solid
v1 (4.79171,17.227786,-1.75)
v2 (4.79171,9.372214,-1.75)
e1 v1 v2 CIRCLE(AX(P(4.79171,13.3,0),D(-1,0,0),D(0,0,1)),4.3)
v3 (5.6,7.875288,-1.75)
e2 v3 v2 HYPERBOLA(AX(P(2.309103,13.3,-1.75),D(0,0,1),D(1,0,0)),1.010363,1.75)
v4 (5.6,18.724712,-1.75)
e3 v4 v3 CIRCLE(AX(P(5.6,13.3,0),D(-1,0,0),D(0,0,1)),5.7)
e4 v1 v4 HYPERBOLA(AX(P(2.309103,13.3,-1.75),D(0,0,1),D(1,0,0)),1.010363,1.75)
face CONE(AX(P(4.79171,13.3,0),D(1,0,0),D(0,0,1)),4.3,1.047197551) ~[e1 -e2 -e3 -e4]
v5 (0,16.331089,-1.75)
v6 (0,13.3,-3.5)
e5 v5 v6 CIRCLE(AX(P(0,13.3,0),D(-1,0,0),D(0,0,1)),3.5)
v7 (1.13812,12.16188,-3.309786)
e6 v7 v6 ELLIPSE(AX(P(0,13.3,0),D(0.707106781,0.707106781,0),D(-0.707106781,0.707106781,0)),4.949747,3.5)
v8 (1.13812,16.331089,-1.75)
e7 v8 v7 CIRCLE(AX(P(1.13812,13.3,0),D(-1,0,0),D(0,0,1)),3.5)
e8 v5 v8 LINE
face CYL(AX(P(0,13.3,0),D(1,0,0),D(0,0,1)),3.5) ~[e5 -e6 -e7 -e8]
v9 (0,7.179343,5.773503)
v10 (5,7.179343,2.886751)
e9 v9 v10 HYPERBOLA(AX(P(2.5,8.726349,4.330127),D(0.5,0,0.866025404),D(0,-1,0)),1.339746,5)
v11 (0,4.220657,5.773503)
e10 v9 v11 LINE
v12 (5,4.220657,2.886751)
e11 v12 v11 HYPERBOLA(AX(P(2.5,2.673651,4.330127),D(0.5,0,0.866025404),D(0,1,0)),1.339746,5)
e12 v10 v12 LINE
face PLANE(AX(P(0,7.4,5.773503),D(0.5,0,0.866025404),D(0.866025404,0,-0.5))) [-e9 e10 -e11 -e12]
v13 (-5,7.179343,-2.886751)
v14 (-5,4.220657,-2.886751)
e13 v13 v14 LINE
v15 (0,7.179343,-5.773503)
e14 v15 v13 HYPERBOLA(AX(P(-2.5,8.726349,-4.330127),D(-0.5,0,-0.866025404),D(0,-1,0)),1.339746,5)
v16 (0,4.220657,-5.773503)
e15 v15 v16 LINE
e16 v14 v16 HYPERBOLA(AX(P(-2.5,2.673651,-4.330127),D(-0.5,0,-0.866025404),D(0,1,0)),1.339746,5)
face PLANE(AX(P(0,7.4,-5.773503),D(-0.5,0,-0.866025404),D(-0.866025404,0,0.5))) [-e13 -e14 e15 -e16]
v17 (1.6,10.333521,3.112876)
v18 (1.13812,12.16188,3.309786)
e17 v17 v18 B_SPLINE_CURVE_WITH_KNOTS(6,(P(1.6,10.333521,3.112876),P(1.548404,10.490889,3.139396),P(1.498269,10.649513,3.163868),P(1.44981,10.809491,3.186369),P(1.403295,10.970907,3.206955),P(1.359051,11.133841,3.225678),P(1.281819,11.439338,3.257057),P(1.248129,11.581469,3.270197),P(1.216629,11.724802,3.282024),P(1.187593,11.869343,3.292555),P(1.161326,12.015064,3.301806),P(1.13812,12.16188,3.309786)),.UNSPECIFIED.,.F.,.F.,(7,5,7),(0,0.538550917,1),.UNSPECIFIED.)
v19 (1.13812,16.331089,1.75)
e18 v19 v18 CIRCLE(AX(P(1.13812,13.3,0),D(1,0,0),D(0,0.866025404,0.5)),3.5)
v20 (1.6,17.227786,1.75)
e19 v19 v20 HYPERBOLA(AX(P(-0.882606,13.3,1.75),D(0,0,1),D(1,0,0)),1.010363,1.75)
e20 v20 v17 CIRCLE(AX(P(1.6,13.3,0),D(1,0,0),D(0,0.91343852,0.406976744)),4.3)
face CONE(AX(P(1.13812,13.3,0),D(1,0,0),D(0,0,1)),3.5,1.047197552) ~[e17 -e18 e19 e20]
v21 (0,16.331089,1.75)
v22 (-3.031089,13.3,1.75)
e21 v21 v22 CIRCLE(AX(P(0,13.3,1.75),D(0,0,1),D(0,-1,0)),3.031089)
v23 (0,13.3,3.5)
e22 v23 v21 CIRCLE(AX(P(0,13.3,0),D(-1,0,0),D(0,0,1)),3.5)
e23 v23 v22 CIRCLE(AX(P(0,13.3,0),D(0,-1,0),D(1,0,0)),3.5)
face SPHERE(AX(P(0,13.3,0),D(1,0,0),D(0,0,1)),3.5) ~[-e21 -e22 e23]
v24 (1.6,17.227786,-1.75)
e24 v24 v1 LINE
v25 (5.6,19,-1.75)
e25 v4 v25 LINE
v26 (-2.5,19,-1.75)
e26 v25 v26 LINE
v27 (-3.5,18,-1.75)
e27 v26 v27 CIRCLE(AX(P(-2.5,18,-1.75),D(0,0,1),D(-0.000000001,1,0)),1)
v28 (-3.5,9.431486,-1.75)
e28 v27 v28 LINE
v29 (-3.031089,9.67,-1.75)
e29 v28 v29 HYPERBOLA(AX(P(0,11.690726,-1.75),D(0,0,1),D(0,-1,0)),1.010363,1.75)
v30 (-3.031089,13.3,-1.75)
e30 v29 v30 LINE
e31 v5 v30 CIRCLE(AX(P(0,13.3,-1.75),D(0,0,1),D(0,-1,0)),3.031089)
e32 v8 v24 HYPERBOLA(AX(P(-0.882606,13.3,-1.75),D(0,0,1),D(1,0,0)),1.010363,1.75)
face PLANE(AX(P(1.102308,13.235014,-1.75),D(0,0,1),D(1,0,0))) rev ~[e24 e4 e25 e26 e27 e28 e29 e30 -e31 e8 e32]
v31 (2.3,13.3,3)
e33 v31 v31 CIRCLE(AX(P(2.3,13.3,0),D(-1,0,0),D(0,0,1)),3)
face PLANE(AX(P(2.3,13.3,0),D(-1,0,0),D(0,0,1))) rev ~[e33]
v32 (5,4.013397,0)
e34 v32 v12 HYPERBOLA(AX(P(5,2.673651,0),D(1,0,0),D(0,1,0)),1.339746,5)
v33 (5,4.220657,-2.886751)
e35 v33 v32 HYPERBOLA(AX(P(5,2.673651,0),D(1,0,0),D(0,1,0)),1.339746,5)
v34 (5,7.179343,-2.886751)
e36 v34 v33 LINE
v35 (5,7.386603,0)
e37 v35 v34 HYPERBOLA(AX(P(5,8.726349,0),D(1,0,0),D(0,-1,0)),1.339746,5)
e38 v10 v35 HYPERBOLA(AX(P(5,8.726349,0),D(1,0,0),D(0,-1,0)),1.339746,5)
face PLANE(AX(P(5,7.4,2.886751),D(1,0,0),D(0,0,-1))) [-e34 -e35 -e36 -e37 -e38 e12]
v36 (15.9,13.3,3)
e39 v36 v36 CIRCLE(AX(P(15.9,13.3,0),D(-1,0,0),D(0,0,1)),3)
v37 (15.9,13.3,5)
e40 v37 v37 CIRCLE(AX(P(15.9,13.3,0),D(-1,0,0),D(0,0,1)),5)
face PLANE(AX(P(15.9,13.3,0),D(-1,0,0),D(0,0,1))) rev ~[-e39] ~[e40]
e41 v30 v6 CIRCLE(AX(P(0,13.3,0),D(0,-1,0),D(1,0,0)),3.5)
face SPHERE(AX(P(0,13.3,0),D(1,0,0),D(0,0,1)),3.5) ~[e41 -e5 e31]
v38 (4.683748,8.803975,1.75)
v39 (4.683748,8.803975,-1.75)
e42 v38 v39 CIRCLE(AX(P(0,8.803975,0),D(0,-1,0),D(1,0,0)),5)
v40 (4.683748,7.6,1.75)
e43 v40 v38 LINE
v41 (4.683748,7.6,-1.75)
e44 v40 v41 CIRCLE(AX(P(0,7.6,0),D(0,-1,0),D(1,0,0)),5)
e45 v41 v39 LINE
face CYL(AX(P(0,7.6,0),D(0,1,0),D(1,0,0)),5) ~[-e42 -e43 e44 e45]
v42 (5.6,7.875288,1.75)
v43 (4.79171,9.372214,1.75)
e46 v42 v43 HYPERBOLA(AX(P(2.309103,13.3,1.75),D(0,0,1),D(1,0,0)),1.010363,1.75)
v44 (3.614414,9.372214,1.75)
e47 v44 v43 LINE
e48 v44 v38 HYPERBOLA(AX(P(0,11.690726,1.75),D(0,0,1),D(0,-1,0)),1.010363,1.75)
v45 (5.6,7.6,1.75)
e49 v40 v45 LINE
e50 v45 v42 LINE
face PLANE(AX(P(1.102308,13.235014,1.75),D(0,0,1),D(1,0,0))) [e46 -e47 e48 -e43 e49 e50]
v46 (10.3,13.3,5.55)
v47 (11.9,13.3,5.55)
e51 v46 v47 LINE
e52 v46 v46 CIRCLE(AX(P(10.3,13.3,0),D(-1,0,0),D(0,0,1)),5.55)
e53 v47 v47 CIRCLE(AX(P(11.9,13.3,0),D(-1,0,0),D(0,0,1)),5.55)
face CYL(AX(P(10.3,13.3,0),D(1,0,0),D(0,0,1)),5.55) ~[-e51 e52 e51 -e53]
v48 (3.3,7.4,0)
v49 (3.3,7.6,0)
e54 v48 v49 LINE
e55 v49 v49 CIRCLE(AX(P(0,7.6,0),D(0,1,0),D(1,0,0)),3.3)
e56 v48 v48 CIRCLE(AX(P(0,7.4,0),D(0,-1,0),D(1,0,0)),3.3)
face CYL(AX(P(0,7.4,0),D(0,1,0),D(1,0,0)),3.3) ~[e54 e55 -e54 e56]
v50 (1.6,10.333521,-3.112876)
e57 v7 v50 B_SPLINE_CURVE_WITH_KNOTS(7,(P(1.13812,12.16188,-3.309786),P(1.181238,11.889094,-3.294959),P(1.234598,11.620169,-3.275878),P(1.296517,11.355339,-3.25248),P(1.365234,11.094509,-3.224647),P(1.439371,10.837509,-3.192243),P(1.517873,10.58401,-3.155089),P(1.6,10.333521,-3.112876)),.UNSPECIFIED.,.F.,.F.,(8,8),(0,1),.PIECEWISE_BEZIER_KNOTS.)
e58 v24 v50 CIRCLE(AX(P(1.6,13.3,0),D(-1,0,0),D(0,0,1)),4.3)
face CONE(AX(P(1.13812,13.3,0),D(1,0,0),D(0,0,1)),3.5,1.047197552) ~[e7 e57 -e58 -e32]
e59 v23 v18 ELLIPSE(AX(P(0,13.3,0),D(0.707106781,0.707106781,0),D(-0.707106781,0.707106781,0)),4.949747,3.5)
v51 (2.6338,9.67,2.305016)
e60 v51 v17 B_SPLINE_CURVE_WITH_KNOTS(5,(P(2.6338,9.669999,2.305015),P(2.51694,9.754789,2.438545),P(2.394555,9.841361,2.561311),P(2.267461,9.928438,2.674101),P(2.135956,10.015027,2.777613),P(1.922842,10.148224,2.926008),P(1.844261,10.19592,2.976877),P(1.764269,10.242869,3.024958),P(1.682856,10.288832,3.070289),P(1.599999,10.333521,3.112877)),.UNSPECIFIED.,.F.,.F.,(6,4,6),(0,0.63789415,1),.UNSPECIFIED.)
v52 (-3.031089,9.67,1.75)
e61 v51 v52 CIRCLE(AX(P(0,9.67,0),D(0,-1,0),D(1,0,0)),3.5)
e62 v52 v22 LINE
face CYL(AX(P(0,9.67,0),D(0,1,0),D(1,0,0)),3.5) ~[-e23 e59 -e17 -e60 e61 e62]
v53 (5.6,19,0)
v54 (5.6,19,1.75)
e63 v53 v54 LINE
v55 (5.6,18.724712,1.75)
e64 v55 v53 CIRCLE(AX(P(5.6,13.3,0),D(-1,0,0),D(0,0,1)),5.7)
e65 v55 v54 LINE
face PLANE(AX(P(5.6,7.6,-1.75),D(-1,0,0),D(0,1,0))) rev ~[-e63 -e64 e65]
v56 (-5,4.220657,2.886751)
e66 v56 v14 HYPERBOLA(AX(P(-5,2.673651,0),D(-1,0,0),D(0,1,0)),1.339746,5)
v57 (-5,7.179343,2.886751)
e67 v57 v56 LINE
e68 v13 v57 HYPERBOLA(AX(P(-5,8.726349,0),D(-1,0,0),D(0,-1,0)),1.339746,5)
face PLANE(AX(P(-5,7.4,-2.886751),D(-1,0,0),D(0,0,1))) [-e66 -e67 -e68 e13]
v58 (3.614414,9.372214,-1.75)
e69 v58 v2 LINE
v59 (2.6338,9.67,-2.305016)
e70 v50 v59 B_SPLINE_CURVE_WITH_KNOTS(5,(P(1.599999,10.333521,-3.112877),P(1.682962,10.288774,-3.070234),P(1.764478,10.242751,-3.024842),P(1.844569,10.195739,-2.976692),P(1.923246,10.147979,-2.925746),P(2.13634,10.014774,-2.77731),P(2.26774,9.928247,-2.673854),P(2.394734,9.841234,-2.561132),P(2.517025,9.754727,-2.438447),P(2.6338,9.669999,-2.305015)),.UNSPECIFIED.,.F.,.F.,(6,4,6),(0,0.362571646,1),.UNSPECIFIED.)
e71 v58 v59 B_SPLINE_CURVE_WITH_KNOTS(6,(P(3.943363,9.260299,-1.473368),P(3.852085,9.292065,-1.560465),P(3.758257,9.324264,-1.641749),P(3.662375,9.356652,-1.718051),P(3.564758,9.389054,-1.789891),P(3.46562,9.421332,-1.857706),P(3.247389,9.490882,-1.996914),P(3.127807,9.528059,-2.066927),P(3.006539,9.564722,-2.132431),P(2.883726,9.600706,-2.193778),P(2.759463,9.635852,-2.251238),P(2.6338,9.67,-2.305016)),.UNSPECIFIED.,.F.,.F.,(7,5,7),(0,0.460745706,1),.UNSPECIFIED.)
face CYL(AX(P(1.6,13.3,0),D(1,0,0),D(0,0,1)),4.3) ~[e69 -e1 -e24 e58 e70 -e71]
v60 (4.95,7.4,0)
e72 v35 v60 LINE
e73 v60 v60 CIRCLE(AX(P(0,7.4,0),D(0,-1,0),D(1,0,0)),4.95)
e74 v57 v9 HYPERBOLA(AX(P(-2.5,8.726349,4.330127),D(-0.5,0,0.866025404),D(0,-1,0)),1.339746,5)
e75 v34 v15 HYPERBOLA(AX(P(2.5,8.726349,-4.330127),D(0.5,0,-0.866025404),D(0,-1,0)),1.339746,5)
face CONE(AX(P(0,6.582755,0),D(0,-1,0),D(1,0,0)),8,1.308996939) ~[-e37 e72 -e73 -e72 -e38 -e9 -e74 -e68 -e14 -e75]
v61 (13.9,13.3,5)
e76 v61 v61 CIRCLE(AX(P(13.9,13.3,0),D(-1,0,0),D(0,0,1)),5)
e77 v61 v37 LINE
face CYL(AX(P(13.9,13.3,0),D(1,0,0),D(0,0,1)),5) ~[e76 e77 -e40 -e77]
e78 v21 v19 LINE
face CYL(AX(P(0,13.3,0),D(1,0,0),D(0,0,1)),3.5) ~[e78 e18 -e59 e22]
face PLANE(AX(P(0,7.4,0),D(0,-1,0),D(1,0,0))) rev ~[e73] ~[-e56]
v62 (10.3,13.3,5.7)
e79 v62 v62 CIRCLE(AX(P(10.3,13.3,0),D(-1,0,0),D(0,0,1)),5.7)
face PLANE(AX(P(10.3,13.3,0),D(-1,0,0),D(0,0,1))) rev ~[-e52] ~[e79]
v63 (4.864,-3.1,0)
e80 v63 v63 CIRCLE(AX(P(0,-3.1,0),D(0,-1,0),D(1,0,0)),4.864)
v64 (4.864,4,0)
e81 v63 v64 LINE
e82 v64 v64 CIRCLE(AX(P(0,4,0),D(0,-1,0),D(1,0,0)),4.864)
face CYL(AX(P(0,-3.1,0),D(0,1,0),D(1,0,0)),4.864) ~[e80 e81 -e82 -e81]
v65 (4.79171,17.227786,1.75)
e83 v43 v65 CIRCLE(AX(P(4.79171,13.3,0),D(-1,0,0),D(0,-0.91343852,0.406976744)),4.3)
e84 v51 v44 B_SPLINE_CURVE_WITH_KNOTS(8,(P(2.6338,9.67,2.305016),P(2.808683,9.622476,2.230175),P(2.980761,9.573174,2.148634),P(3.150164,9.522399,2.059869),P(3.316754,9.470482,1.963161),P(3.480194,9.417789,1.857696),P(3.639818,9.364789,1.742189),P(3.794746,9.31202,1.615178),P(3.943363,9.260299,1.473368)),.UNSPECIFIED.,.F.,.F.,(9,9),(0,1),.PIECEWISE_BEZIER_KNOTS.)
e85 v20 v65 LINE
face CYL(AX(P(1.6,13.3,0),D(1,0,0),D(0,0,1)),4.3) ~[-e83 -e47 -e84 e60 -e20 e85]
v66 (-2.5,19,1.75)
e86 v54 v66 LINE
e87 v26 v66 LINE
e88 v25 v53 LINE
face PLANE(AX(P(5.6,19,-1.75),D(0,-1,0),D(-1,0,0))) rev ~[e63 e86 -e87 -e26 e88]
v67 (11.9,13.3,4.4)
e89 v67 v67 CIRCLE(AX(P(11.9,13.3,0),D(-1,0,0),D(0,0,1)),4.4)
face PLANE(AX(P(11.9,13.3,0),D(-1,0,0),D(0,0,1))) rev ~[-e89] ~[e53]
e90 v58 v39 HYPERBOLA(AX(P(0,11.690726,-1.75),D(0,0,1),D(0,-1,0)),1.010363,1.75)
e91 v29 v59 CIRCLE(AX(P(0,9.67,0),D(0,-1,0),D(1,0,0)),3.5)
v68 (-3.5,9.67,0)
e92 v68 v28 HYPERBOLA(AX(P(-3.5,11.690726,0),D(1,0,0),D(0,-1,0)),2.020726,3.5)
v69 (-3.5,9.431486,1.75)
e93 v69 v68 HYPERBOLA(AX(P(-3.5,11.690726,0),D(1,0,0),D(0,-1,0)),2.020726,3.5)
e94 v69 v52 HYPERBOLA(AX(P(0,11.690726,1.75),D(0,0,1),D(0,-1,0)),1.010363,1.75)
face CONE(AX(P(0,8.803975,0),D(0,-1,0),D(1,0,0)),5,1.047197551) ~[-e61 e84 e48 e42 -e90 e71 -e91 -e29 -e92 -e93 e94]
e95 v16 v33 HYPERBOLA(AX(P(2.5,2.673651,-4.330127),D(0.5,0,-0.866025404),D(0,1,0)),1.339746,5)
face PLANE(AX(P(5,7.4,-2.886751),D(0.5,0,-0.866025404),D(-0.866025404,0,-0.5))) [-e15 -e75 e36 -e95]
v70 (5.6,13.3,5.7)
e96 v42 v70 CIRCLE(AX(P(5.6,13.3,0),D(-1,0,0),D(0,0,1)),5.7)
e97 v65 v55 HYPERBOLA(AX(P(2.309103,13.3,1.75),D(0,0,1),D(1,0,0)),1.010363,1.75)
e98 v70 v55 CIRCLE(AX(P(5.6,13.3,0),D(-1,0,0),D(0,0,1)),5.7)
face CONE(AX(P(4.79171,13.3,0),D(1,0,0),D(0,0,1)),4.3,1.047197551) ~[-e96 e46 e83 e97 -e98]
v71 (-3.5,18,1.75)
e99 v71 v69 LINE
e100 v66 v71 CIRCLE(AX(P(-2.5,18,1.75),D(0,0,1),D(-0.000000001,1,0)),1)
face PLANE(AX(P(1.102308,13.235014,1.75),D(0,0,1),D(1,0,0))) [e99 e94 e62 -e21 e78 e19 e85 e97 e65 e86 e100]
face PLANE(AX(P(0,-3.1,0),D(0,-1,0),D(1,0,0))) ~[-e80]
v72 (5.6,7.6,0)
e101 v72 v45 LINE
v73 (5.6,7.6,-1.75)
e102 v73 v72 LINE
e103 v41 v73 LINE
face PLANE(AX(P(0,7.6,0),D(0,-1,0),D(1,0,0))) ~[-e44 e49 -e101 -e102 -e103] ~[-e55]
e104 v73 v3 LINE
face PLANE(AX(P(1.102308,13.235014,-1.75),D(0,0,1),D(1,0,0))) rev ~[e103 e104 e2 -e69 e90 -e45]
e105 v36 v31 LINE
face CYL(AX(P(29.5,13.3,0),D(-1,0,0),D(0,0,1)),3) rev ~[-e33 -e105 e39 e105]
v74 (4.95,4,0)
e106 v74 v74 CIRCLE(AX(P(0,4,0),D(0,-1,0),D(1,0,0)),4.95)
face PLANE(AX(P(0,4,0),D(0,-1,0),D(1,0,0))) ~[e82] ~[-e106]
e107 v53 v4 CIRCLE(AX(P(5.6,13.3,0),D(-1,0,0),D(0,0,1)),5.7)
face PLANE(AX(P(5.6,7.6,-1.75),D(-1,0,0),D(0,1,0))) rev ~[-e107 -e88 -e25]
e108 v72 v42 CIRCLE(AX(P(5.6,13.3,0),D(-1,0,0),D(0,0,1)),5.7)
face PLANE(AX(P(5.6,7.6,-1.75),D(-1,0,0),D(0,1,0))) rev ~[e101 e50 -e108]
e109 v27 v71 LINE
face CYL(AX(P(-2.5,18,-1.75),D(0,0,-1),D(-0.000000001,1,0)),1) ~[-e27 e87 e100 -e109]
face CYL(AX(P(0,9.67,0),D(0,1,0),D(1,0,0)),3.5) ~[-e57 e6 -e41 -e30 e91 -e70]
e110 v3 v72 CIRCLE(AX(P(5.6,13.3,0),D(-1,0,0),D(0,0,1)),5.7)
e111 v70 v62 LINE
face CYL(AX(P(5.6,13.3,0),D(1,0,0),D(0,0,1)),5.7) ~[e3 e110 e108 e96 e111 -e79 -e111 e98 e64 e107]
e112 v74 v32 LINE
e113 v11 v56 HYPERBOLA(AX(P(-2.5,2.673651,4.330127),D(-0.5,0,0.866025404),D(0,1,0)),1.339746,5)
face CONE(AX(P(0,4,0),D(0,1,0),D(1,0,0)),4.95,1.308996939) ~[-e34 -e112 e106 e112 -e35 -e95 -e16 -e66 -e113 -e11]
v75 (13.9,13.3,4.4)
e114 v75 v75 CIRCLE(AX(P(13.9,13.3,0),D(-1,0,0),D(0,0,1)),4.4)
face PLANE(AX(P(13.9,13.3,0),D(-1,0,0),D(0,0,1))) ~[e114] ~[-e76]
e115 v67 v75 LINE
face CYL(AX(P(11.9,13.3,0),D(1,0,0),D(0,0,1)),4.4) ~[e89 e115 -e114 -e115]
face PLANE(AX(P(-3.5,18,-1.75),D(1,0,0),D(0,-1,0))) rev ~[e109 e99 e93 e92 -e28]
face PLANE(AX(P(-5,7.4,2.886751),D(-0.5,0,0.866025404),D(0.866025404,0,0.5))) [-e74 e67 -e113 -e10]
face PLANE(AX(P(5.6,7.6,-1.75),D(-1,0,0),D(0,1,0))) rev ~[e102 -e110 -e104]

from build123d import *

# Parameters (mm, degrees)
BOSS_EXTRUDE1_DEPTH      = 1.75
BOSS_EXTRUDE1_DEPTH_BACK = 1.75
SKETCH3_R                = 23.447488612
CUT_EXTRUDE1_DEPTH       = 3.4
HOLE1_D                  = 6
HOLE1_DEPTH              = 13.6


with BuildPart() as part:
    # Sketch1 → Revolve1 (revolve)
    with BuildSketch(Plane.XY, mode=Mode.PRIVATE) as revolve1_sk:
        Polygon((0, -3.1), (-4.864, -3.1), (-4.864, 4), (-4.95, 4), (-8, 4.817245037), (-8, 6.582754963), (-4.95, 7.4), (-3.3, 7.4), (-3.3, 7.6), (-5, 7.6), (-5, 8.803974596), (-3.5, 9.67), (-3.5, 13.3), (0, 13.3), align=None)
    revolve(revolve1_sk.sketch.rotate(Axis((0, 13.3, 0), (0, -1, 0)), 180), axis=Axis((0, 13.3, 0), (0, -1, 0)))

    # Sketch2 → Boss-Extrude1 (add, two sides: drawn at the far end of the back side and taken through both)
    with BuildSketch(Plane.XY.offset(-BOSS_EXTRUDE1_DEPTH_BACK)):
        with BuildLine():
            Line((-3.5, 7.6), (5.6, 7.6))
            Line((5.6, 7.6), (5.6, 19))
            Line((5.6, 19), (-2.5, 19))
            ThreePointArc((-2.5, 19), (-3.207106781, 18.707106781), (-3.5, 18))
            Line((-3.5, 18), (-3.5, 7.6))
        make_face()
    extrude(amount=BOSS_EXTRUDE1_DEPTH + BOSS_EXTRUDE1_DEPTH_BACK)

    # Sketch3 → Cut-Extrude1 (cut)
    with BuildSketch(Plane(origin=(0, 7.4, 0), x_dir=(1, 0, 0), z_dir=(0, 1, 0))):
        Circle(SKETCH3_R)
        Polygon((-5, 2.886751346), (-5, -2.886751346), (0, -5.773502692), (5, -2.886751346), (5, 2.886751346), (0, 5.773502692), align=None, mode=Mode.SUBTRACT)
    extrude(amount=-CUT_EXTRUDE1_DEPTH, mode=Mode.SUBTRACT)

    # Sketch4 → Revolve2 (revolve)
    with BuildSketch(Plane.XY, mode=Mode.PRIVATE) as revolve2_sk:
        with BuildLine():
            Line((0, 16.8), (1.138119785, 16.8))
            Line((1.138119785, 16.8), (1.6, 17.6))
            Line((1.6, 17.6), (4.791709623, 17.6))
            Line((4.791709623, 17.6), (5.6, 19))
            Line((5.6, 19), (10.3, 19))
            Line((10.3, 19), (10.3, 18.85))
            Line((10.3, 18.85), (11.9, 18.85))
            Line((11.9, 18.85), (11.9, 17.7))
            Line((11.9, 17.7), (13.9, 17.7))
            Line((13.9, 17.7), (13.9, 18.3))
            Line((13.9, 18.3), (15.9, 18.3))
            Line((15.9, 18.3), (15.9, 13.3))
            Line((15.9, 13.3), (-3.5, 13.3))
            ThreePointArc((-3.5, 13.3), (-2.474873734, 15.774873734), (0, 16.8))
        make_face()
    revolve(revolve2_sk.sketch.rotate(Axis((15.9, 13.3, 0), (-1, 0, 0)), 270), axis=Axis((15.9, 13.3, 0), (-1, 0, 0)))

    # Hole1
    with Locations(Plane(origin=(15.9, 0, 0), x_dir=(0, 0, -1), z_dir=(1, 0, 0))):
        with Locations((0, 13.3)):
            Hole(HOLE1_D / 2, depth=HOLE1_DEPTH)


solid = part.part
